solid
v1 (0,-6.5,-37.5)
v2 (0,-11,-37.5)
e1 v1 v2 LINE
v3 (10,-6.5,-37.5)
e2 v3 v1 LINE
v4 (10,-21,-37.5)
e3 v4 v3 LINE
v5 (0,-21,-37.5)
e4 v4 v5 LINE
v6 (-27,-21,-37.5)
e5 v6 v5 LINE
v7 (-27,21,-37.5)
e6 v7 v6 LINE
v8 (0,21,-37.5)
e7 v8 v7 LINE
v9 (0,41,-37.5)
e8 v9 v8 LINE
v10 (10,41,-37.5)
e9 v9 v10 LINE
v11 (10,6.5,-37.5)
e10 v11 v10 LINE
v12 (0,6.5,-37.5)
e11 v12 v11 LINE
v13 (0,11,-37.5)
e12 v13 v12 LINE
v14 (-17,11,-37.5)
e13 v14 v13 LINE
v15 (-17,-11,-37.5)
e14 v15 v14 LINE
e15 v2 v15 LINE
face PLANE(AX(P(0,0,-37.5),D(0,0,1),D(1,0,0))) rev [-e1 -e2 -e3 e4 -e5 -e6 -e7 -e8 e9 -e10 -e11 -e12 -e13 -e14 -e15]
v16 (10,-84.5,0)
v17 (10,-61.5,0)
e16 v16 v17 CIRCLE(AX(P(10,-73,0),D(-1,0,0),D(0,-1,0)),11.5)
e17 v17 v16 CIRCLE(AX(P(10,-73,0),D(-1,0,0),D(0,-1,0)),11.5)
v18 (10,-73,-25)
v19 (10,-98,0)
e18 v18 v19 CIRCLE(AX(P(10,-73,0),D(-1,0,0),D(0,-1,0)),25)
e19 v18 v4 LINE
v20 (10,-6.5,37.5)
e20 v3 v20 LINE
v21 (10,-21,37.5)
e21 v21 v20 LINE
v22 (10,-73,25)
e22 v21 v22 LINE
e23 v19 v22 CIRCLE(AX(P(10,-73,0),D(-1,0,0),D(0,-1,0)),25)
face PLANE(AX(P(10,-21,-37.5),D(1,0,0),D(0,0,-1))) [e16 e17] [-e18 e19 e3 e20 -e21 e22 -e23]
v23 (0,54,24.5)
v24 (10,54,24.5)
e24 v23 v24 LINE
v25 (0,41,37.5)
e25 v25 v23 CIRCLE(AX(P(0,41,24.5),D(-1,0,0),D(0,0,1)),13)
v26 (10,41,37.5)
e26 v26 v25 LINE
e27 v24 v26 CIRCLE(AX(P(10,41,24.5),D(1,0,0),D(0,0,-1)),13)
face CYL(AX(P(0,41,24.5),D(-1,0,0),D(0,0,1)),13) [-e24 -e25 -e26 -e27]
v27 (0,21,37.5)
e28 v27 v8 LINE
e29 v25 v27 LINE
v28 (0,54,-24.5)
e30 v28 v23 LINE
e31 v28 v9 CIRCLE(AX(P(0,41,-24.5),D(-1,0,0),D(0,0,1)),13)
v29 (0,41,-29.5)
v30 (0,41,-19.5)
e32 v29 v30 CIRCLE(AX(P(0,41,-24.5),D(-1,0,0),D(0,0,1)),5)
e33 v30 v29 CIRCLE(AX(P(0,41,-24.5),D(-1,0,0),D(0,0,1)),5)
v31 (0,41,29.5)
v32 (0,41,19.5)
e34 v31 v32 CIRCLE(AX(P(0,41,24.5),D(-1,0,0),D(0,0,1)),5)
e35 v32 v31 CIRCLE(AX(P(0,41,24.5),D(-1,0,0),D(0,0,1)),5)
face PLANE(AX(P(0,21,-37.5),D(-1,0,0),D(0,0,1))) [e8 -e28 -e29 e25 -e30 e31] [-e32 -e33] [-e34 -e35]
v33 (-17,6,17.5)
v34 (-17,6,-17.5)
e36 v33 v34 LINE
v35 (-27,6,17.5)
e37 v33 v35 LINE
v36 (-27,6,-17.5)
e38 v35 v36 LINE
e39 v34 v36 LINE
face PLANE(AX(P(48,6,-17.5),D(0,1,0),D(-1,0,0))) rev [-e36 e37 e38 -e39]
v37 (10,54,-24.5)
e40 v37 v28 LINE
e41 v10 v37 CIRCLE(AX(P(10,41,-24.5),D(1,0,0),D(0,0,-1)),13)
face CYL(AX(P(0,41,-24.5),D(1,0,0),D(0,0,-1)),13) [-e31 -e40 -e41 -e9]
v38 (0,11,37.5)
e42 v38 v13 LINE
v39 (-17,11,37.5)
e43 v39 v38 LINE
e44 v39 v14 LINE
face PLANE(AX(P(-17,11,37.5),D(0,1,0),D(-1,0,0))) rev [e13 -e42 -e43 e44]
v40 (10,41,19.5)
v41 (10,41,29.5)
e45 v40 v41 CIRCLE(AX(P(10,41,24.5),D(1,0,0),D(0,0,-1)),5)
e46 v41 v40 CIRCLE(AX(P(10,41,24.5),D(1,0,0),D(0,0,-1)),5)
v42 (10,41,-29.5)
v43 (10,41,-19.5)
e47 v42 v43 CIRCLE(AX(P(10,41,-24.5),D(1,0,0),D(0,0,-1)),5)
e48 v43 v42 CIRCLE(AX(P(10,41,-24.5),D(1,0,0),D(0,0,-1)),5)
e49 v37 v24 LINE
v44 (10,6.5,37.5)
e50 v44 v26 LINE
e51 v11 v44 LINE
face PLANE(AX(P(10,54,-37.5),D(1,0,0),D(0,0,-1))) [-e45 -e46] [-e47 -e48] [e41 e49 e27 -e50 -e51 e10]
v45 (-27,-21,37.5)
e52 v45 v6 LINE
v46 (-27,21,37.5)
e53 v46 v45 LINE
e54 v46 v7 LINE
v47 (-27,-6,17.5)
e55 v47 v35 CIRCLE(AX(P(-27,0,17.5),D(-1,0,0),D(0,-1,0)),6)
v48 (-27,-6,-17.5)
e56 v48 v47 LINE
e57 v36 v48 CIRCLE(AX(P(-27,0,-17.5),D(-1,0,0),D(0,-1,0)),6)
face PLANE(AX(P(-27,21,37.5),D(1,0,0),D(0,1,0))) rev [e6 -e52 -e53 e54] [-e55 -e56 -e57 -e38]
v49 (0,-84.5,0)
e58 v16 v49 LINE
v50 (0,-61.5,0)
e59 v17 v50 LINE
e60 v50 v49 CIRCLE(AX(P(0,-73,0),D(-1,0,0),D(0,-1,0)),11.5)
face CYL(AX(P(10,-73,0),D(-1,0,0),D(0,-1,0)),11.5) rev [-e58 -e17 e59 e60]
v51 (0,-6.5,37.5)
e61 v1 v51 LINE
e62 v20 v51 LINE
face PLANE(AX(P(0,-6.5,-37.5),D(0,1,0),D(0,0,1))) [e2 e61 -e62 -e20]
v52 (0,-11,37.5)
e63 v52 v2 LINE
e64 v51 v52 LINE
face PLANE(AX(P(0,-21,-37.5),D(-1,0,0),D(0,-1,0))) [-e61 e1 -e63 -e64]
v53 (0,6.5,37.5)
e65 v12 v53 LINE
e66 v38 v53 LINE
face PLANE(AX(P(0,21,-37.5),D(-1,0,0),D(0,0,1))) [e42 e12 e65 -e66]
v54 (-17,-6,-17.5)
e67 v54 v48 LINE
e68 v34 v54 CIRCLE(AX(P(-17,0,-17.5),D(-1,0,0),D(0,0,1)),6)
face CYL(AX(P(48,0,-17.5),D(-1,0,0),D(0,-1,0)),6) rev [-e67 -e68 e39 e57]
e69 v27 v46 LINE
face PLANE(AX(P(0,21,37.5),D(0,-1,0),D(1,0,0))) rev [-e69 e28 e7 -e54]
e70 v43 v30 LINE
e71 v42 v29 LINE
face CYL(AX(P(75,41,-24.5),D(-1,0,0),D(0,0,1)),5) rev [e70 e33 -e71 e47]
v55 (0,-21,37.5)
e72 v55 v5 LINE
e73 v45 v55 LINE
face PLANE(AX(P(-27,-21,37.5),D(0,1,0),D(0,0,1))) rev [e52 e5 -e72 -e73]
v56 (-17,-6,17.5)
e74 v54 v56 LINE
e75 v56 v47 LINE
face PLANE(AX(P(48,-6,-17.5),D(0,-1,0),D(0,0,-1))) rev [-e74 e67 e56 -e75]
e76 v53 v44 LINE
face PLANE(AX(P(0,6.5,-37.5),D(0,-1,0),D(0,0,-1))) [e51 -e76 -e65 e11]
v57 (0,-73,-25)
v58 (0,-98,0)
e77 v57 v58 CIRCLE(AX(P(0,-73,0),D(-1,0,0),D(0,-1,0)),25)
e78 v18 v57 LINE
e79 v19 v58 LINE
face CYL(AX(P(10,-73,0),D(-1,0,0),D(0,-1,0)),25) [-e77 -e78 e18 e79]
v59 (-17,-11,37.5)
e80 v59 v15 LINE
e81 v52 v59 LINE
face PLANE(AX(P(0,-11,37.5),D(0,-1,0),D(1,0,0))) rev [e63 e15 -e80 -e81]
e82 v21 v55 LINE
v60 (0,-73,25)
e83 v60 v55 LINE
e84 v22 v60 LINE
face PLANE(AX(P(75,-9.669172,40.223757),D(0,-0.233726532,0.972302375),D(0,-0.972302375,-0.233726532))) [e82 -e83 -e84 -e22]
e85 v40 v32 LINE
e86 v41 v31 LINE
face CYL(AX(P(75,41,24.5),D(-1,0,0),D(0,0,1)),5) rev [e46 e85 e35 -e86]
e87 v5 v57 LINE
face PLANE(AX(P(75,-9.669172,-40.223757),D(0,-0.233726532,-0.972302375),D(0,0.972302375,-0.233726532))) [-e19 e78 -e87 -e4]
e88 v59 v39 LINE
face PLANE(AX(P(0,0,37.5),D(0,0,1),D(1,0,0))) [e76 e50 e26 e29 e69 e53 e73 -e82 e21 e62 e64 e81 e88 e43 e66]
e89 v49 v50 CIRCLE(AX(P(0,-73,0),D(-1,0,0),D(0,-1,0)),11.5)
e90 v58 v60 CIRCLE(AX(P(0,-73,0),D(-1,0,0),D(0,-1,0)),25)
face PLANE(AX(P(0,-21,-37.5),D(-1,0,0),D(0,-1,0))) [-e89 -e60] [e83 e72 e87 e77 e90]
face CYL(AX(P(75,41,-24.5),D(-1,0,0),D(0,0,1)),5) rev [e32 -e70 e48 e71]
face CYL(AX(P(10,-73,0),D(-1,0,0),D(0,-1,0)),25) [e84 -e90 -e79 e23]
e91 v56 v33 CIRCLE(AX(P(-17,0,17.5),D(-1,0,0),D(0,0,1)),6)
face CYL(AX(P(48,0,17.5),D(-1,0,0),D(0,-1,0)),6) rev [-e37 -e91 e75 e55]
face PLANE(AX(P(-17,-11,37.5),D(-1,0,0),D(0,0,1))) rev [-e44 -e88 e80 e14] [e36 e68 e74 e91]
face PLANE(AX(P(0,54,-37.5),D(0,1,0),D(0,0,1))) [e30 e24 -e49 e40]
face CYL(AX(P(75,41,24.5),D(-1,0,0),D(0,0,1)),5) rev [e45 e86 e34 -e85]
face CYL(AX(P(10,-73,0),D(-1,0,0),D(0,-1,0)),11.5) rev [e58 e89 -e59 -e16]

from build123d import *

# Parameters (mm, degrees)
BASE_BODY_DEPTH              = 37.5
UPPER_FLANGE_DEPTH           = 75
FLANGE_CORNER_FILLET_R13_A_R = 13
FLANGE_CORNER_FILLET_R13_B_R = 13
MOUNTING_HOLES_SKETCH_R      = 5
MOUNTING_HOLES_2X_10_DEPTH   = 75
SLOT_6MM_DEPTH               = 75
HANGER_PLATE_DEPTH           = 75
TAPER_CUT_DEPTH              = 75
EYE_BOSS_SKETCH_R            = 25
EYE_BOSS_DEPTH               = 10
EYE_HOLE_SKETCH_R            = 11.5
EYE_HOLE_23_DEPTH            = 10


with BuildPart() as part:
    # Base Profile Sketch → Base Body (new, symmetric)
    with BuildSketch(Plane.XY):
        Polygon((0, 11), (0, 21), (-27, 21), (-27, -21), (0, -21), (0, -11), (-17, -11), (-17, 11), align=None)
    extrude(amount=BASE_BODY_DEPTH, both=True)

    # Upper Flange Sketch → Upper Flange (add)
    with BuildSketch(Plane.XY.offset(37.5)):
        Polygon((0, 21), (0, 54), (10, 54), (10, 21), (10, 6.5), (0, 6.5), align=None)
    extrude(amount=-UPPER_FLANGE_DEPTH)

    # Flange Corner Fillet R13 A
    flange_corner_fillet_r13_a_edges = [part.edges().sort_by_distance(p)[0] for p in [
        (5, 54, 37.5),
    ]]
    fillet(flange_corner_fillet_r13_a_edges, radius=FLANGE_CORNER_FILLET_R13_A_R)

    # Flange Corner Fillet R13 B
    flange_corner_fillet_r13_b_edges = [part.edges().sort_by_distance(p)[0] for p in [
        (5, 54, -37.5),
    ]]
    fillet(flange_corner_fillet_r13_b_edges, radius=FLANGE_CORNER_FILLET_R13_B_R)

    # Mounting Holes Sketch → Mounting Holes 2xØ10 (cut)
    with BuildSketch(Plane.ZY):
        with Locations((24.5, 41)):
            Circle(MOUNTING_HOLES_SKETCH_R)
        with Locations((-24.5, 41)):
            Circle(MOUNTING_HOLES_SKETCH_R)
    extrude(amount=-MOUNTING_HOLES_2X_10_DEPTH, mode=Mode.SUBTRACT)

    # Slot Sketch → Slot 6mm (cut)
    with BuildSketch(Plane.ZY.offset(27)):
        with BuildLine():
            Line((-17.5, 6), (17.5, 6))
            ThreePointArc((17.5, 6), (23.5, 0), (17.5, -6))
            Line((17.5, -6), (-17.5, -6))
            ThreePointArc((-17.5, -6), (-23.5, 0), (-17.5, 6))
        make_face()
    extrude(amount=-SLOT_6MM_DEPTH, mode=Mode.SUBTRACT)

    # Hanger Plate Sketch → Hanger Plate (add)
    with BuildSketch(Plane.XY.offset(37.5)):
        Polygon((0, -6.5), (0, -21), (0, -73), (10, -73), (10, -21), (10, -6.5), align=None)
    extrude(amount=-HANGER_PLATE_DEPTH)

    # Taper Cut Sketch → Taper Cut (cut)
    with BuildSketch(Plane.ZY):
        Polygon((37.5, -73), (37.5, -21), (25, -73), align=None)
        Polygon((-25, -73), (-37.5, -21), (-37.5, -73), align=None)
    extrude(amount=-TAPER_CUT_DEPTH, mode=Mode.SUBTRACT)

    # Eye Boss Sketch → Eye Boss (add)
    with BuildSketch(Plane.ZY):
        with Locations((0, -73)):
            Circle(EYE_BOSS_SKETCH_R)
    extrude(amount=-EYE_BOSS_DEPTH)

    # Eye Hole Sketch → Eye Hole Ø23 (cut)
    with BuildSketch(Plane.ZY):
        with Locations(Location((0, -73, 0), (0, 0, 270))):
            Circle(EYE_HOLE_SKETCH_R)
    extrude(amount=-EYE_HOLE_23_DEPTH, mode=Mode.SUBTRACT)


solid = part.part
